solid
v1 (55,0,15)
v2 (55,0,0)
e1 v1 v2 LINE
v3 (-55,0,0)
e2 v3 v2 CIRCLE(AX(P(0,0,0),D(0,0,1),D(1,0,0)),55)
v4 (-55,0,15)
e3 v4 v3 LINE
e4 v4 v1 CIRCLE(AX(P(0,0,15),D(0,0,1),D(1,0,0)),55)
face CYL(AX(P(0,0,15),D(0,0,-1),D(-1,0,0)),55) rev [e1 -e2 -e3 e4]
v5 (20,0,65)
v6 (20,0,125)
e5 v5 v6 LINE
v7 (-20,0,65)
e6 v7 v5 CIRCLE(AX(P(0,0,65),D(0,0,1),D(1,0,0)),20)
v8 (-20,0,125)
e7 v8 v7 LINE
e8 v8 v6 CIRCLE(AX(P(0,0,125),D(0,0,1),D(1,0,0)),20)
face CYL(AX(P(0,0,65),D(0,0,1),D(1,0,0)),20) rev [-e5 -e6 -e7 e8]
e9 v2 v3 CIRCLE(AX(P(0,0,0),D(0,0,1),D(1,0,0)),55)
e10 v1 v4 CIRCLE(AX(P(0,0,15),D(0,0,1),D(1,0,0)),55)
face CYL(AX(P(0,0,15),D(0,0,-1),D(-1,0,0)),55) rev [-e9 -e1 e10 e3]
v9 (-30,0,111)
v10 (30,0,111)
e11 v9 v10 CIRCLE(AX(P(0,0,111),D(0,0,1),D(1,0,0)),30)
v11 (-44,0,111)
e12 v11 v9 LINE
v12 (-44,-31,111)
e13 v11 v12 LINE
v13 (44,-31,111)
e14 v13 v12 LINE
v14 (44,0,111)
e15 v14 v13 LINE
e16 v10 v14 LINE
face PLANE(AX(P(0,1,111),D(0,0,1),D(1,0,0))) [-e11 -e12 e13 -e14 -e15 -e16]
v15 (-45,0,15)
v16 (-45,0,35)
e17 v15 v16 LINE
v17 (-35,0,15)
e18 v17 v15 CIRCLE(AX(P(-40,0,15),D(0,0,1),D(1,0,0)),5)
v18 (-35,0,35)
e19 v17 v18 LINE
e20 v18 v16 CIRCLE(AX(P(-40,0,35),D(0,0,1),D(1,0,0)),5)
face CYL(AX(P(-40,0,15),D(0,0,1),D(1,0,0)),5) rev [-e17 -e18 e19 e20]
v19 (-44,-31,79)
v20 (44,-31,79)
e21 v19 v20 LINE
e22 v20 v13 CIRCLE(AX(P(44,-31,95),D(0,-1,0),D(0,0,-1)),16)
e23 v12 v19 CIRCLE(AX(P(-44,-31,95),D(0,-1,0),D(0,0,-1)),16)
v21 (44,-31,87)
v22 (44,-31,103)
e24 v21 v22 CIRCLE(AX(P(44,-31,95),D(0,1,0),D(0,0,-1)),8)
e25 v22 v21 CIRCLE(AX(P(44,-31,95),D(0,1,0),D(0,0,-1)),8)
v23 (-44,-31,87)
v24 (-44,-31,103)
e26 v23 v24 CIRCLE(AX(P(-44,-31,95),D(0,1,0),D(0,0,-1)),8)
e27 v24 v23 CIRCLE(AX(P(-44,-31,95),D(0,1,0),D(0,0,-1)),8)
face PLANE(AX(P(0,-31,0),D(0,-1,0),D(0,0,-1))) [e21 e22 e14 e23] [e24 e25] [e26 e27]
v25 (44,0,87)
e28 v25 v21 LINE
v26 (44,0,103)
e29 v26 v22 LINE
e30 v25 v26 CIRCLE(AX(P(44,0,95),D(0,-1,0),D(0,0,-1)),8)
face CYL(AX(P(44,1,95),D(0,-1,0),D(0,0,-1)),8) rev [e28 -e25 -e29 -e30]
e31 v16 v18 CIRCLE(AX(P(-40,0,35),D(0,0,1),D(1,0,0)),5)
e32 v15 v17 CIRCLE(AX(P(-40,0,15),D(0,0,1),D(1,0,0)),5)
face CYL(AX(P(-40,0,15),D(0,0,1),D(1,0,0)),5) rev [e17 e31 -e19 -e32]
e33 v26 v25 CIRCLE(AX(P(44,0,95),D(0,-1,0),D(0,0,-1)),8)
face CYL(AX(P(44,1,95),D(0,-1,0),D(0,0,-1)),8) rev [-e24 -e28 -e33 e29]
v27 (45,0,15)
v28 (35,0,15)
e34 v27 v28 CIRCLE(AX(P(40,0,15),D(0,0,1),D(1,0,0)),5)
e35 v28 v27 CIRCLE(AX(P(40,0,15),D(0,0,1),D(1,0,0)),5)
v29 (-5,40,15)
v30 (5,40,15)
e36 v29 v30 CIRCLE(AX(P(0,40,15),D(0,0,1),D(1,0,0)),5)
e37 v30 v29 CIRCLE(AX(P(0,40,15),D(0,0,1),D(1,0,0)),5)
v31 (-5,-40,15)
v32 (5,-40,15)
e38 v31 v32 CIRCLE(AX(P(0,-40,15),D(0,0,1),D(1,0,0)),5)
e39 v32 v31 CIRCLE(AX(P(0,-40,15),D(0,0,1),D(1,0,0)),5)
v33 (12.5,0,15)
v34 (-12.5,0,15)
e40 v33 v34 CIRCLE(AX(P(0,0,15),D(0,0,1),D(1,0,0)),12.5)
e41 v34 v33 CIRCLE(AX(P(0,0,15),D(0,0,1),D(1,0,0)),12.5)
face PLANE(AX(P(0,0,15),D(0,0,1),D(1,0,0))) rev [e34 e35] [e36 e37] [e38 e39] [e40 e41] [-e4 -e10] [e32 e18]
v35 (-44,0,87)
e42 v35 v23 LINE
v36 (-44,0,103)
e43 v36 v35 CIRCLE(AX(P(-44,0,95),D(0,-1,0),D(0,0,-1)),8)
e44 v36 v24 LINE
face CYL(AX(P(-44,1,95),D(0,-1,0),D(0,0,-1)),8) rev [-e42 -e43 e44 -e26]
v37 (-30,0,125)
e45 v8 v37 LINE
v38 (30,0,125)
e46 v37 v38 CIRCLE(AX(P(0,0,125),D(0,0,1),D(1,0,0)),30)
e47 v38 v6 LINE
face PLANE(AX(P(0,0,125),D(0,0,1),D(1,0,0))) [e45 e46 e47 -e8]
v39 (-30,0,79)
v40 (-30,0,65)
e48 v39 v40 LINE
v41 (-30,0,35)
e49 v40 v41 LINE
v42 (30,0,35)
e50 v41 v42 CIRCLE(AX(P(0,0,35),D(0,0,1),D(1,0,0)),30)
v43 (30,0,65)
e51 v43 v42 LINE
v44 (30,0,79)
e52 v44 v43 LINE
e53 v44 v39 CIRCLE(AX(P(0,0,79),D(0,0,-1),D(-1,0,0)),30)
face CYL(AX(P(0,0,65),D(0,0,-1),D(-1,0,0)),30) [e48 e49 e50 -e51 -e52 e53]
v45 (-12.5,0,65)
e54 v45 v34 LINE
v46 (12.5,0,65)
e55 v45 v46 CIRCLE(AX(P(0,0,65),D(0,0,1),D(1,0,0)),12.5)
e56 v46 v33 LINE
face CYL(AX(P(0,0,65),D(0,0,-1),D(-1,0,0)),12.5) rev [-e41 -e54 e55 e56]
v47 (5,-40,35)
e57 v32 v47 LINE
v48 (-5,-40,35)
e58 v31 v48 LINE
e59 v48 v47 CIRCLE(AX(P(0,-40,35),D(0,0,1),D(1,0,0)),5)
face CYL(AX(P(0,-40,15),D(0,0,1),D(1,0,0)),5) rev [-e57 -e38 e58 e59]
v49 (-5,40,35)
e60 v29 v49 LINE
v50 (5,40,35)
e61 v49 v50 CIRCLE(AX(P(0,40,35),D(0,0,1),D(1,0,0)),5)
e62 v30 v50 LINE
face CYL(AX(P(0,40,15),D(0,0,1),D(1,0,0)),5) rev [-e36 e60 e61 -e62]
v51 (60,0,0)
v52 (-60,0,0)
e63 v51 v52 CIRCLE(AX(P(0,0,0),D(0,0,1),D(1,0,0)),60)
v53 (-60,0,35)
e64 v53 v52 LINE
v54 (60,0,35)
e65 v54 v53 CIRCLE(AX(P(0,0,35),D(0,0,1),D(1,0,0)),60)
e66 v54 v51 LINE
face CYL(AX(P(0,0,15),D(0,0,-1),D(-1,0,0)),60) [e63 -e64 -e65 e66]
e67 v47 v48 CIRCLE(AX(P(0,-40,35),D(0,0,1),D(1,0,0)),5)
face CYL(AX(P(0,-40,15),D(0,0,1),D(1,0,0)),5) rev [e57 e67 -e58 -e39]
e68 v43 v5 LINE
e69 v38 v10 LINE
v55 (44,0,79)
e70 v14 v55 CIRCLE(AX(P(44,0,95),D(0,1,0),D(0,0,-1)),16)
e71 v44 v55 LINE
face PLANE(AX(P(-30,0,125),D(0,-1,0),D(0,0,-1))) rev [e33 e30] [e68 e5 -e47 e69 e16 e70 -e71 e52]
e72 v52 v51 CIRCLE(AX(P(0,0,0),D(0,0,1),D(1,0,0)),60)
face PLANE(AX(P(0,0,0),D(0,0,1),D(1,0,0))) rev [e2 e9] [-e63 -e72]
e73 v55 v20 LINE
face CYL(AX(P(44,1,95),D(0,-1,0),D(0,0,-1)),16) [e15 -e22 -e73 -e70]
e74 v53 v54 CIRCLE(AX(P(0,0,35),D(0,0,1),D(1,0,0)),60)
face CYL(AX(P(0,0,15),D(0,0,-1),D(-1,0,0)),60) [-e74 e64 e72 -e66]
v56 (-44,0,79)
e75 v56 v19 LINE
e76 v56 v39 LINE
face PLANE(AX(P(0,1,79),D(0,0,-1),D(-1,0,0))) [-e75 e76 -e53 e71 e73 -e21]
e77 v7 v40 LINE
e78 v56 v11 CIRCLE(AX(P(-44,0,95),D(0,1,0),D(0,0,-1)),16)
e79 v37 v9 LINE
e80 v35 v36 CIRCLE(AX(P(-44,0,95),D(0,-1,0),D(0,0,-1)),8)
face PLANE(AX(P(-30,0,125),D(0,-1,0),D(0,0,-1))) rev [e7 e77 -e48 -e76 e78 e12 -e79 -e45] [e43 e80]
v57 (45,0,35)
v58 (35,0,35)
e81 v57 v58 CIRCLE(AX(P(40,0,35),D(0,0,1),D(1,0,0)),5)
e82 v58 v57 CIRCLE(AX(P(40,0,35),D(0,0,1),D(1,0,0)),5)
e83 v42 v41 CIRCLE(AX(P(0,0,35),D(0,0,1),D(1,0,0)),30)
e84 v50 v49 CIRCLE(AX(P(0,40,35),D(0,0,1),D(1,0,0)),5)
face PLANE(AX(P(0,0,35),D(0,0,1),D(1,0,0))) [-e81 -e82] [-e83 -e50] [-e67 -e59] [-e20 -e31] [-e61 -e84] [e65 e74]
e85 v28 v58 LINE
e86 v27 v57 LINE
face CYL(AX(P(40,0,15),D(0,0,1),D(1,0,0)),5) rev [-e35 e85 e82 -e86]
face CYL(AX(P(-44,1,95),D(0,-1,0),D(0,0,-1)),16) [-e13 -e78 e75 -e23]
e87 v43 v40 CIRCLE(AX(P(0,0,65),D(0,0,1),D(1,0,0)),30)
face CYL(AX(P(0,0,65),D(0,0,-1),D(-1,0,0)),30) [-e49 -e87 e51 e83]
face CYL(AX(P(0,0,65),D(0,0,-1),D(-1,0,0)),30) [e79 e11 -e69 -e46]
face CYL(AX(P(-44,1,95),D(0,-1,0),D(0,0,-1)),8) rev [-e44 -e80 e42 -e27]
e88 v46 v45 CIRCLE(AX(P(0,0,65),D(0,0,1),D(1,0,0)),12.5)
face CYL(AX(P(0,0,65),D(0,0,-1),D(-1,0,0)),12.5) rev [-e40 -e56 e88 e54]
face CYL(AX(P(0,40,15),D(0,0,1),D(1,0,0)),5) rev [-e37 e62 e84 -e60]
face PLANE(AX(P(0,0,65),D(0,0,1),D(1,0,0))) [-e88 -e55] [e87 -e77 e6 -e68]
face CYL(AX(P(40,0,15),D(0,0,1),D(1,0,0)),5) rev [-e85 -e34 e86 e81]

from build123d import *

# Parameters (mm, degrees)
BASE_FLANGE_SKETCH_R              = 60
BASE_FLANGE_SKETCH_R_2            = 55
BASE_FLANGE_PLATE_DEPTH           = 15
ROUND_FLANGE_SKETCH_120_R         = 60
ROUND_FLANGE_120_DEPTH            = 20
FLANGE_BOLT_HOLES_SKETCH_R        = 5
FLANGE_BOLT_HOLES_4X_10_DEPTH     = 20
HUB_BOSS_SKETCH_R                 = 30
HUB_BOSS_SKETCH_R_2               = 12.5
HUB_BOSS_DEPTH                    = 30
HUB_START                         = -30
HUB_BORE_SKETCH_25_R              = 12.5
HUB_BORE_25_DEPTH                 = 30
CRADLE_BODY_DEPTH                 = 60
CRADLE_LUGS_SKETCH_R              = 16
CRADLE_LUGS_SKETCH_R_2            = 8
CRADLE_MOUNTING_LUGS_DEPTH        = 31
CRADLE_BORE_SKETCH_40_R           = 20
CRADLE_BORE_40_DEPTH              = 60
LUG_PAD_SKETCH_R                  = 8
LUG_PADS_DEPTH                    = 32
PARTING_SLOT_SKETCH_W             = 120
PARTING_SLOT_SKETCH_H             = 1
CRADLE_PARTING_SLOT_1MM_DEPTH     = 32
LUG_BORE_SKETCH_40_R              = 20
CRADLE_BORE_40_THROUGH_LUGS_DEPTH = 60


with BuildPart() as part:
    # Base Flange Sketch → Base Flange Plate (new body)
    with BuildSketch(Plane.XY):
        Circle(BASE_FLANGE_SKETCH_R)
        Circle(BASE_FLANGE_SKETCH_R_2, mode=Mode.SUBTRACT)
    extrude(amount=BASE_FLANGE_PLATE_DEPTH)

    # Round Flange Sketch Ø120 → Round Flange Ø120 (add)
    with BuildSketch(Plane.XY.offset(15)):
        Circle(ROUND_FLANGE_SKETCH_120_R)
    extrude(amount=ROUND_FLANGE_120_DEPTH)

    # Flange Bolt Holes Sketch → Flange Bolt Holes 4xØ10 (cut)
    with BuildSketch(Plane.XY.offset(35)):
        with Locations((0, 40)):
            Circle(FLANGE_BOLT_HOLES_SKETCH_R)
        with Locations((40, 0)):
            Circle(FLANGE_BOLT_HOLES_SKETCH_R)
        with Locations((0, -40)):
            Circle(FLANGE_BOLT_HOLES_SKETCH_R)
        with Locations((-40, 0)):
            Circle(FLANGE_BOLT_HOLES_SKETCH_R)
    extrude(amount=-FLANGE_BOLT_HOLES_4X_10_DEPTH, mode=Mode.SUBTRACT)

    # Hub Boss Sketch → Hub Boss (add)
    with BuildSketch(Plane.XY.offset(35)):
        Circle(HUB_BOSS_SKETCH_R)
        Circle(HUB_BOSS_SKETCH_R_2, mode=Mode.SUBTRACT)
    extrude(amount=HUB_BOSS_DEPTH)

    # Hub Bore Sketch Ø25 → Hub Bore Ø25 (cut)
    with BuildSketch(Plane.XY.offset(35).offset(HUB_START)):
        Circle(HUB_BORE_SKETCH_25_R)
    extrude(amount=HUB_BORE_25_DEPTH, mode=Mode.SUBTRACT)

    # Cradle Body Sketch → Cradle Body (add)
    with BuildSketch(Plane.XY.offset(65)):
        with BuildLine():
            Line((-30, 0), (-12.5, 0))
            ThreePointArc((-12.5, 0), (0, -12.5), (12.5, 0))
            Line((12.5, 0), (30, 0))
            ThreePointArc((30, 0), (0, -30), (-30, 0))
        make_face()
    extrude(amount=CRADLE_BODY_DEPTH)


with BuildPart() as body_2:
    # Cradle Lugs Sketch → Cradle Mounting Lugs (new body)
    # profile 1 of 6: a face of its own
    with BuildSketch(Plane(origin=(0, 0, 0), x_dir=(1, 0, 0), z_dir=(0, 1, 0))):
        with Locations((-44, -95)):
            Circle(CRADLE_LUGS_SKETCH_R)
        with Locations(Location((-44, -95, 0), (0, 0, 270))):
            Circle(CRADLE_LUGS_SKETCH_R_2, mode=Mode.SUBTRACT)
    # profile 2 of 6: a face of its own
    with BuildSketch(Plane(origin=(0, 0, 0), x_dir=(1, 0, 0), z_dir=(0, 1, 0))):
        with BuildLine():
            Line((-12.5, -79), (-44, -79))
            ThreePointArc((-44, -79), (-32.686291501, -83.686291501), (-28, -95))
            ThreePointArc((-28, -95), (-32.686291501, -106.313708499), (-44, -111))
            Line((-44, -111), (-12.5, -111))
            Line((-12.5, -111), (12.5, -111))
            Line((12.5, -111), (12.5, -79))
            Line((12.5, -79), (-12.5, -79))
        make_face()
    # profile 3 of 6: a face of its own
    with BuildSketch(Plane(origin=(0, 0, 0), x_dir=(1, 0, 0), z_dir=(0, 1, 0))):
        with BuildLine():
            Line((30, -79), (12.5, -79))
            Line((12.5, -79), (12.5, -111))
            Line((12.5, -111), (30, -111))
            Line((30, -111), (30, -102.745966692))
            ThreePointArc((30, -102.745966692), (28, -95), (30, -87.254033308))
            Line((30, -87.254033308), (30, -79))
        make_face()
    # profile 4 of 6: a face of its own
    with BuildSketch(Plane(origin=(0, 0, 0), x_dir=(1, 0, 0), z_dir=(0, 1, 0))):
        with BuildLine():
            Line((44, -79), (30, -79))
            Line((30, -79), (30, -87.254033308))
            ThreePointArc((30, -87.254033308), (35.873975975, -81.217121725), (44, -79))
        make_face()
    # profile 5 of 6: a face of its own
    with BuildSketch(Plane(origin=(0, 0, 0), x_dir=(1, 0, 0), z_dir=(0, 1, 0))):
        with BuildLine():
            Line((30, -102.745966692), (30, -111))
            Line((30, -111), (44, -111))
            ThreePointArc((44, -111), (35.873975975, -108.782878275), (30, -102.745966692))
        make_face()
    # profile 6 of 6: a face of its own
    with BuildSketch(Plane(origin=(0, 0, 0), x_dir=(1, 0, 0), z_dir=(0, 1, 0))):
        with BuildLine():
            ThreePointArc((60, -95), (55.313708499, -83.686291501), (44, -79))
            ThreePointArc((44, -79), (35.873975975, -81.217121725), (30, -87.254033308))
            Line((30, -87.254033308), (30, -102.745966692))
            ThreePointArc((30, -102.745966692), (35.873975975, -108.782878275), (44, -111))
            ThreePointArc((44, -111), (55.313708499, -106.313708499), (60, -95))
        make_face()
        with Locations(Location((44, -95, 0), (0, 0, 270))):
            Circle(CRADLE_LUGS_SKETCH_R_2, mode=Mode.SUBTRACT)
    extrude(amount=-CRADLE_MOUNTING_LUGS_DEPTH)


with BuildPart() as cradle_bore_40_tool:
    # Cradle Bore Sketch Ø40 → Cradle Bore Ø40 (new body)
    with BuildSketch(Plane.XY.offset(125)):
        Circle(CRADLE_BORE_SKETCH_40_R)
    extrude(amount=-CRADLE_BORE_40_DEPTH)


with BuildPart() as part_1:
    add(part.part)

    # Cradle Bore Ø40: cut by cradle_bore_40_tool
    add(cradle_bore_40_tool.part, mode=Mode.SUBTRACT)



with BuildPart() as body_2_1:
    add(body_2.part)

    # Cradle Bore Ø40: cut by cradle_bore_40_tool
    add(cradle_bore_40_tool.part, mode=Mode.SUBTRACT)


with BuildPart() as part_2:
    add(part_1.part)

    add(body_2_1.part)  # Lug Pads merges body 2
    # Lug Pad Sketch → Lug Pads (add)
    # profile 1 of 4: a face of its own
    with BuildSketch(Plane.XZ.offset(31)):
        with BuildLine():
            ThreePointArc((-28, 95), (-32.686291501, 106.313708499), (-44, 111))
            ThreePointArc((-44, 111), (-60, 95), (-44, 79))
            ThreePointArc((-44, 79), (-32.686291501, 83.686291501), (-28, 95))
        make_face()
        with Locations(Location((-44, 95, 0), (0, 0, 270))):
            Circle(LUG_PAD_SKETCH_R, mode=Mode.SUBTRACT)
    # profile 2 of 4: a face of its own
    with BuildSketch(Plane.XZ.offset(31)):
        with BuildLine():
            Line((44, 111), (-44, 111))
            ThreePointArc((-44, 111), (-32.686291501, 106.313708499), (-28, 95))
            ThreePointArc((-28, 95), (-32.686291501, 83.686291501), (-44, 79))
            Line((-44, 79), (44, 79))
            ThreePointArc((44, 79), (35.873975975, 81.217121725), (30, 87.254033308))
            ThreePointArc((30, 87.254033308), (28, 95), (30, 102.745966692))
            ThreePointArc((30, 102.745966692), (35.873975975, 108.782878275), (44, 111))
        make_face()
    # profile 3 of 4: a face of its own
    with BuildSketch(Plane.XZ.offset(31)):
        with BuildLine():
            ThreePointArc((30, 87.254033308), (28, 95), (30, 102.745966692))
            Line((30, 102.745966692), (30, 87.254033308))
        make_face()
    # profile 4 of 4: a face of its own
    with BuildSketch(Plane.XZ.offset(31)):
        with BuildLine():
            ThreePointArc((60, 95), (55.313708499, 106.313708499), (44, 111))
            ThreePointArc((44, 111), (35.873975975, 108.782878275), (30, 102.745966692))
            Line((30, 102.745966692), (30, 87.254033308))
            ThreePointArc((30, 87.254033308), (35.873975975, 81.217121725), (44, 79))
            ThreePointArc((44, 79), (55.313708499, 83.686291501), (60, 95))
        make_face()
        with Locations(Location((44, 95, 0), (0, 0, 270))):
            Circle(LUG_PAD_SKETCH_R, mode=Mode.SUBTRACT)
    extrude(amount=-LUG_PADS_DEPTH)

    # Parting Slot Sketch → Cradle Parting Slot 1mm (cut)
    with BuildSketch(Plane.XY.offset(111)):
        with Locations((0, 0.5)):
            Rectangle(PARTING_SLOT_SKETCH_W, PARTING_SLOT_SKETCH_H)
    extrude(amount=-CRADLE_PARTING_SLOT_1MM_DEPTH, mode=Mode.SUBTRACT)

    # Lug Bore Sketch Ø40 → Cradle Bore Ø40 Through Lugs (cut)
    with BuildSketch(Plane.XY.offset(125)):
        Circle(LUG_BORE_SKETCH_40_R)
    extrude(amount=-CRADLE_BORE_40_THROUGH_LUGS_DEPTH, mode=Mode.SUBTRACT)


solid = part_2.part
